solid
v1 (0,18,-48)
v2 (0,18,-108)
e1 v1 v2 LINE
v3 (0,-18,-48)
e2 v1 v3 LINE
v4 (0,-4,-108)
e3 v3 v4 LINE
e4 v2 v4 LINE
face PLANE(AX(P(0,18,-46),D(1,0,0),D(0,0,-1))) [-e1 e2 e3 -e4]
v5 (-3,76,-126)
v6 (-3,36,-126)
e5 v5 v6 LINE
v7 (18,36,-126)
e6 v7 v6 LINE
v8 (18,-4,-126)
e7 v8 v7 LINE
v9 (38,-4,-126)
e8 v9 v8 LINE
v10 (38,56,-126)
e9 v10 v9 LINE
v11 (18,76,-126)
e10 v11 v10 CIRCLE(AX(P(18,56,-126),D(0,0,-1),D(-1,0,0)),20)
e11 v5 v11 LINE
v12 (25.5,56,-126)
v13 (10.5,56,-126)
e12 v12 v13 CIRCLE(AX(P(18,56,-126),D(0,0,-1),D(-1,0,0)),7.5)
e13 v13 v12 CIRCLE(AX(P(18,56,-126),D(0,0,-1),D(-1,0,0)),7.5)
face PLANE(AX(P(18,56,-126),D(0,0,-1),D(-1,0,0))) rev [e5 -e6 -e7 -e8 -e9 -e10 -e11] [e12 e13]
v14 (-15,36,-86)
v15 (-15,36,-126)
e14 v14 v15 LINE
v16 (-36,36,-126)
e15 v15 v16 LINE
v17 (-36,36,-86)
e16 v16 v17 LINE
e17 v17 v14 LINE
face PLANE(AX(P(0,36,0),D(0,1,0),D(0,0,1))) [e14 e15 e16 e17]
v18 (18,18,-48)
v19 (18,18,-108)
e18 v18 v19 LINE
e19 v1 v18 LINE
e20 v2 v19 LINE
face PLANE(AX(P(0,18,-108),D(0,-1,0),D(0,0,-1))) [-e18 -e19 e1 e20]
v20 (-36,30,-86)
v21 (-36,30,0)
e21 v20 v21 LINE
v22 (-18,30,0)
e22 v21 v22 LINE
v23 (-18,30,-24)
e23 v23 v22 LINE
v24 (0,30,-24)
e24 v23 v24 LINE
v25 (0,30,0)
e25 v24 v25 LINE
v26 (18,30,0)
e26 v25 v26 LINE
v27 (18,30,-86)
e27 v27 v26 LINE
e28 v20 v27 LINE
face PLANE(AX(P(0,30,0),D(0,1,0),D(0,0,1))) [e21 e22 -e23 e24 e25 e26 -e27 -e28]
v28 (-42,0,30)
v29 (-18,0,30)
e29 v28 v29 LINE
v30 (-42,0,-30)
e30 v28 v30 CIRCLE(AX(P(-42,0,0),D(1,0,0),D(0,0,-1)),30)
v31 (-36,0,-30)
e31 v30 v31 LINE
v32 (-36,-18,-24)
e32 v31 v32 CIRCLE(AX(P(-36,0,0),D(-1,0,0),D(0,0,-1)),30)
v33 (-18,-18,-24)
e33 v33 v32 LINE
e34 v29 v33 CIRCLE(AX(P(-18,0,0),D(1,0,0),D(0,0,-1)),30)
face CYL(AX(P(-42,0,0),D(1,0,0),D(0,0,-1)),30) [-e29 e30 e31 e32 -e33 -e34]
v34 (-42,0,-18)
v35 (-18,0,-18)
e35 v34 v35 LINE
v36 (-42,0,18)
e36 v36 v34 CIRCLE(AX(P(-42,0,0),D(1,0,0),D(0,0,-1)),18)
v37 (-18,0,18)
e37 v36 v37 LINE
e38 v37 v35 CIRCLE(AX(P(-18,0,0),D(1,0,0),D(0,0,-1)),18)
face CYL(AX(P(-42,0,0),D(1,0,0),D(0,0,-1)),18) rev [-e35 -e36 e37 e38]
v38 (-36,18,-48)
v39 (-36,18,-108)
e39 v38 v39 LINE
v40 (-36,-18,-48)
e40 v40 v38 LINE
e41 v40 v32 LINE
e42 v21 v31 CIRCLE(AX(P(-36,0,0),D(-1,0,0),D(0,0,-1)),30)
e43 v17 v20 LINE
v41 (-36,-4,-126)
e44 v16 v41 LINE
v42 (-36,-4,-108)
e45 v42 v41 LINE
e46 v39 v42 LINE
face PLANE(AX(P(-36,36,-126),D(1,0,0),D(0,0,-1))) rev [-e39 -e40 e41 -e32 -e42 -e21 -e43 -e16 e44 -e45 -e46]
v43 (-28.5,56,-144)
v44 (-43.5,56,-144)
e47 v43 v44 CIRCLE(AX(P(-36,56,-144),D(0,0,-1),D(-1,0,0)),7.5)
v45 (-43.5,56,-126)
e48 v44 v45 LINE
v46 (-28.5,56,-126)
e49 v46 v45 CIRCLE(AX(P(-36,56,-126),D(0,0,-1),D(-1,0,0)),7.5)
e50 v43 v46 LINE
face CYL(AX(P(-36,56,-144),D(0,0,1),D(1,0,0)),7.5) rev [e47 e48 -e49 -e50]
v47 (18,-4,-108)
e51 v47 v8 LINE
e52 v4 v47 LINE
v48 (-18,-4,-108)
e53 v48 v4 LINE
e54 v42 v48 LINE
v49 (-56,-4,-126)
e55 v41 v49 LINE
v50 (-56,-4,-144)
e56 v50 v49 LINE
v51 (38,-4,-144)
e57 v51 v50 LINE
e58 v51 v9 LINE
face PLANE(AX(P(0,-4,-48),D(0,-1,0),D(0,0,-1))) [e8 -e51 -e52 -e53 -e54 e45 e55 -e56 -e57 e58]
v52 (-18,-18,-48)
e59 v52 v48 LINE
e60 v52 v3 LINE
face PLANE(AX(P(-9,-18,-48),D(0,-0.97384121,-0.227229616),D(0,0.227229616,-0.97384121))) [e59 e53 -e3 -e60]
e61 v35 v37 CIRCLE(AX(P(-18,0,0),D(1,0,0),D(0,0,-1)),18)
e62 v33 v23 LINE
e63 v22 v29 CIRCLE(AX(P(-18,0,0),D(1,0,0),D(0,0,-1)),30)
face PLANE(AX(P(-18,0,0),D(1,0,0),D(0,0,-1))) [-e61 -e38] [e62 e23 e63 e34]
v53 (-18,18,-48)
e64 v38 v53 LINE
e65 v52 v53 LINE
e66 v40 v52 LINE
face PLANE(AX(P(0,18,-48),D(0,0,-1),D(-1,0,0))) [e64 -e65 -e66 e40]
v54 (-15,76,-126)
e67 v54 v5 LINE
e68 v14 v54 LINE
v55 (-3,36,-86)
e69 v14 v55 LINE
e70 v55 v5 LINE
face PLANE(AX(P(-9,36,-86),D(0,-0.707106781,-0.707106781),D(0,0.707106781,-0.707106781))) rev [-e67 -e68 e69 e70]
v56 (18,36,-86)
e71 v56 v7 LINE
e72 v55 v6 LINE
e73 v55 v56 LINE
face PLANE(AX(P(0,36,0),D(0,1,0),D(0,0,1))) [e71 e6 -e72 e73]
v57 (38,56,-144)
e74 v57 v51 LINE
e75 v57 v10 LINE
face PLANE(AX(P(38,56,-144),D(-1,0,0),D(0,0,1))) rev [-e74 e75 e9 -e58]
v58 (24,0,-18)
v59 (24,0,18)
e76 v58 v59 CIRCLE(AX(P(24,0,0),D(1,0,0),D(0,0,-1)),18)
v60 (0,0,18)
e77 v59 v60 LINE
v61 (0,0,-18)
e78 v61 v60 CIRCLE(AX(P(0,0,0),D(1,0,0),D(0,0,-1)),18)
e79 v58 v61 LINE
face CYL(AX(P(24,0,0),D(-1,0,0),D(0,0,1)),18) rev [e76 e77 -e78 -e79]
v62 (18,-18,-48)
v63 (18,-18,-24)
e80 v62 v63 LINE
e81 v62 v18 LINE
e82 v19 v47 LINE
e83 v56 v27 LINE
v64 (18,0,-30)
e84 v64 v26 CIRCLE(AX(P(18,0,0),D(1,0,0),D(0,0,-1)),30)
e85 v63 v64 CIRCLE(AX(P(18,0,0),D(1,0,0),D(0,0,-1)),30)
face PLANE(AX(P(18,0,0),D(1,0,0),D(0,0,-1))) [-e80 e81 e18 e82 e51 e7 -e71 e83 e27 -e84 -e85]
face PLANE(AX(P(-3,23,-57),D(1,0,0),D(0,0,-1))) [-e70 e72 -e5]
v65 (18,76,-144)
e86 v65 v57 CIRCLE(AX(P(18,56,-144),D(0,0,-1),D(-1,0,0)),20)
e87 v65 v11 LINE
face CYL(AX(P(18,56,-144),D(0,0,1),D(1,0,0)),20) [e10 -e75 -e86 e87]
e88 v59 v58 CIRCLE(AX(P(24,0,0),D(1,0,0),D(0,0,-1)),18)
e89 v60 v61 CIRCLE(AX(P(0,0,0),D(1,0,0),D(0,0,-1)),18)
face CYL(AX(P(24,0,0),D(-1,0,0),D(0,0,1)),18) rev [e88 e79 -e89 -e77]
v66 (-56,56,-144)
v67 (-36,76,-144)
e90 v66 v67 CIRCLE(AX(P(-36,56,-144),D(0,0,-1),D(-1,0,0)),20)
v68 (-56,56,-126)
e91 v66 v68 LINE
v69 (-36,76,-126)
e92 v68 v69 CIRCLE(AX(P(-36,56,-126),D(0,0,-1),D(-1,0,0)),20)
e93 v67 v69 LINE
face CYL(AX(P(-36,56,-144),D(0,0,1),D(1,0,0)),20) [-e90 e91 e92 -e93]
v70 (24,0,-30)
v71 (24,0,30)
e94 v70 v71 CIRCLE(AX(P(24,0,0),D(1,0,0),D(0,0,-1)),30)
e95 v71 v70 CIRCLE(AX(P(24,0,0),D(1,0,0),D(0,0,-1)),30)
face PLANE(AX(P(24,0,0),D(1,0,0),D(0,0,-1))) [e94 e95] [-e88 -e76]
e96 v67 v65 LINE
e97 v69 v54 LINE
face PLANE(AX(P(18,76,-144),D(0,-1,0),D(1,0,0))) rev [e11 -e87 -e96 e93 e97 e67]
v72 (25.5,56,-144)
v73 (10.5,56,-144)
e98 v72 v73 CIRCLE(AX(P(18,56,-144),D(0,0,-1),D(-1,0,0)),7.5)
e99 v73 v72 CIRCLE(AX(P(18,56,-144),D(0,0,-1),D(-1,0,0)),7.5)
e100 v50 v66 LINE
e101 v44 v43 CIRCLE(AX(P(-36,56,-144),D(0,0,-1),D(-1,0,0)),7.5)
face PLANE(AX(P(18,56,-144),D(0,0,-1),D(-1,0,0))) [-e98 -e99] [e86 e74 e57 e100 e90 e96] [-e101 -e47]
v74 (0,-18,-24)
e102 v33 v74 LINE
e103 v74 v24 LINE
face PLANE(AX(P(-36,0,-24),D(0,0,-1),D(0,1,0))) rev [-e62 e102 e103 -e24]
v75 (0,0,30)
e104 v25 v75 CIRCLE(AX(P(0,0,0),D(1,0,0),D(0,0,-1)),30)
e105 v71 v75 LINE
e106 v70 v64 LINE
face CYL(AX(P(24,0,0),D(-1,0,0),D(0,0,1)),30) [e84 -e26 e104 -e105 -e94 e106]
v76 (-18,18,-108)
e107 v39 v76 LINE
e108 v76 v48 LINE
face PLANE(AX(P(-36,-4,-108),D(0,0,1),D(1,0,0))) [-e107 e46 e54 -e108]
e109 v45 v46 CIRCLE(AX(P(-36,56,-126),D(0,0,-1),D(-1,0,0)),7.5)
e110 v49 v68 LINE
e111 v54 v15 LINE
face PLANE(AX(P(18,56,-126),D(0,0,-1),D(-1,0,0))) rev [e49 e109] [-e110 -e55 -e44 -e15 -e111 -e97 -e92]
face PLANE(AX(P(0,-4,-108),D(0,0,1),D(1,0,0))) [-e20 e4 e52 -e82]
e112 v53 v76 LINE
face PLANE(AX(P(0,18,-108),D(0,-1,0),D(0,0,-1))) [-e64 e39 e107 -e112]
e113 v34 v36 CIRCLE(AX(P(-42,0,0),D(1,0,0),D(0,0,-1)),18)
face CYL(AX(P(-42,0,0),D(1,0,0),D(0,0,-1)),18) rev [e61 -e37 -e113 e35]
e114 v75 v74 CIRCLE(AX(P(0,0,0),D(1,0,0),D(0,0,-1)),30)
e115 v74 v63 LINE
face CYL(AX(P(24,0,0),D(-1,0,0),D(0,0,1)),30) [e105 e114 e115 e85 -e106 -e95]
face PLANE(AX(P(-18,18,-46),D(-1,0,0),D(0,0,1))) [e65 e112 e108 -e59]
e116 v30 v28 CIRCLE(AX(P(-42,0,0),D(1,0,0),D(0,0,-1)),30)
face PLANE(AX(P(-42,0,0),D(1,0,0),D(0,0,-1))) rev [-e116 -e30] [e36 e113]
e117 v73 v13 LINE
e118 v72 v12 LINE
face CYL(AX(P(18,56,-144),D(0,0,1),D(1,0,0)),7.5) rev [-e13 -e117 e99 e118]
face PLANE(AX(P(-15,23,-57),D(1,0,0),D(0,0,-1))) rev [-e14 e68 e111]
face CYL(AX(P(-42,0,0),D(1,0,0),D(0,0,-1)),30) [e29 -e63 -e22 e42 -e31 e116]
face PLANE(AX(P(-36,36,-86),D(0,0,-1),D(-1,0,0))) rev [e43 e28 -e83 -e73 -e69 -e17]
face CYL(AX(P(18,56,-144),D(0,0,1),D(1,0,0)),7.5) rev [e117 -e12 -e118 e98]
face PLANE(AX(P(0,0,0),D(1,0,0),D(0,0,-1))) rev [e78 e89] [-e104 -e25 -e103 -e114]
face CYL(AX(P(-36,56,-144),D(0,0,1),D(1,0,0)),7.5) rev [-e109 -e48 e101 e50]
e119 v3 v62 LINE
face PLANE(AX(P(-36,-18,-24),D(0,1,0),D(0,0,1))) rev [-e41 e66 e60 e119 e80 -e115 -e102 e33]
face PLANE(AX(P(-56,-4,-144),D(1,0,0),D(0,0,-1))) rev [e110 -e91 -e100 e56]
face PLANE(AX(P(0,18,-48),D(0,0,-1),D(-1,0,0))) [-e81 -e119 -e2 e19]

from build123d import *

# Parameters (mm, degrees)
CLEVIS_LUG_A_SKETCH_R       = 30
CLEVIS_LUG_A_SKETCH_R_2     = 18
CLEVIS_LUG_A_60X_36_DEPTH   = 24
CLEVIS_LUG_B_SKETCH_R       = 30
CLEVIS_LUG_B_SKETCH_R_2     = 18
CLEVIS_LUG_B_60X_36_DEPTH   = 24
ARM_START                   = -18
ARM_WEB_DEPTH               = 18
LUG_START                   = -18
LUG_BRIDGE_DEPTH            = 18
ARM_TOP_PLATE_SKETCH_W      = 54
ARM_TOP_PLATE_SKETCH_H      = 40
ARM_TOP_PLATE_6MM_DEPTH     = 6
ARM_SPINE_SKETCH_R          = 4
ARM_SPINE_54MM_DEPTH        = 54
ARM_BODY_SKETCH_W           = 18
ARM_BODY_SKETCH_H           = 22
ARM_BODY_80MM_DEPTH         = 80
ARM_SIDE_WEB_54MM_DEPTH     = 54
ARM_SLOT_SKETCH_W           = 24
ARM_SLOT_SKETCH_H           = 6
ARM_SLOT_CUT_DEPTH          = 27
ARM_RIB_18MM_REACH          = 137.133
ARM_RIB_SKETCH_WALL_W       = 333.878222312
ARM_RIB_SKETCH_WALL_H       = 18
MOUNTING_FLANGE_SKETCH_R    = 7.5
MOUNTING_FLANGE_DEPTH       = 18
FLANGE_GUSSET_12MM_REACH    = 171.473
FLANGE_GUSSET_SKETCH_WALL_W = 397.51396583
FLANGE_GUSSET_SKETCH_WALL_H = 12


with BuildPart() as part:
    # Clevis Lug A Sketch → Clevis Lug A Ø60xØ36 (new body)
    with BuildSketch(Plane(origin=(0, 0, 0), x_dir=(0, 0, -1), z_dir=(1, 0, 0))):
        Circle(CLEVIS_LUG_A_SKETCH_R)
        Circle(CLEVIS_LUG_A_SKETCH_R_2, mode=Mode.SUBTRACT)
    extrude(amount=CLEVIS_LUG_A_60X_36_DEPTH)

    # Arm Web Sketch → Arm Web (add)
    with BuildSketch(Plane(origin=(18, 0, 0), x_dir=(0, 0, -1), z_dir=(1, 0, 0)).offset(ARM_START)):
        with BuildLine():
            Line((0, 30), (48, 30))
            Line((48, 30), (126, 30))
            Line((126, 30), (126, -4))
            Line((126, -4), (108, -4))
            Line((108, -4), (108, 18))
            Line((108, 18), (48, 18))
            Line((48, 18), (48, -4))
            Line((48, -4), (17.549928775, -4))
            ThreePointArc((17.549928775, -4), (14.071247279, 11.22497216), (0, 18))
            Line((0, 18), (0, 30))
        make_face()
    extrude(amount=ARM_WEB_DEPTH)



with BuildPart() as body_2:
    # Clevis Lug B Sketch → Clevis Lug B Ø60xØ36 (new body)
    with BuildSketch(Plane(origin=(-18, 0, 0), x_dir=(0, 0, -1), z_dir=(1, 0, 0))):
        Circle(CLEVIS_LUG_B_SKETCH_R)
        Circle(CLEVIS_LUG_B_SKETCH_R_2, mode=Mode.SUBTRACT)
    extrude(amount=-CLEVIS_LUG_B_60X_36_DEPTH)

    # Lug Bridge Sketch → Lug Bridge (add)
    with BuildSketch(Plane(origin=(-18, 0, 0), x_dir=(0, 0, -1), z_dir=(1, 0, 0)).offset(LUG_START)):
        with BuildLine():
            Line((0, 30), (126, 30))
            Line((126, 30), (126, -4))
            Line((126, -4), (108, -4))
            Line((108, -4), (108, 18))
            Line((108, 18), (48, 18))
            Line((48, 18), (48, -4))
            Line((48, -4), (17.549928775, -4))
            ThreePointArc((17.549928775, -4), (14.071247279, 11.22497216), (0, 18))
            Line((0, 18), (0, 30))
        make_face()
    extrude(amount=LUG_BRIDGE_DEPTH)


with BuildPart() as part_1:
    add(part.part)

    add(body_2.part)  # Arm Top Plate 6mm merges body 2
    # Arm Top Plate Sketch → Arm Top Plate 6mm (add)
    with BuildSketch(Plane(origin=(0, 30, 0), x_dir=(1, 0, 0), z_dir=(0, 1, 0))):
        with Locations((-9, 106)):
            Rectangle(ARM_TOP_PLATE_SKETCH_W, ARM_TOP_PLATE_SKETCH_H)
    extrude(amount=ARM_TOP_PLATE_6MM_DEPTH)

    # Arm Spine Sketch → Arm Spine 54mm (add)
    with BuildSketch(Plane(origin=(18, 0, 0), x_dir=(0, 0, -1), z_dir=(1, 0, 0))):
        with BuildLine():
            ThreePointArc((24, 18), (29.030770743, 7.564016794), (29.732137495, -4))
            Line((29.732137495, -4), (48, -4))
            Line((48, -4), (48, 18))
            Line((48, 18), (108, 18))
            Line((108, 18), (126, 18))
            Line((126, 18), (126, 30))
            Line((126, 30), (86, 30))
            Line((86, 30), (24, 30))
            Line((24, 30), (24, 18))
        make_face()
        with BuildLine():
            Line((24, 18), (24, -4))
            Line((24, -4), (29.732137495, -4))
            ThreePointArc((29.732137495, -4), (29.030770743, 7.564016794), (24, 18))
        make_face()
        Circle(ARM_SPINE_SKETCH_R)
    extrude(amount=-ARM_SPINE_54MM_DEPTH)


with BuildPart() as arm_spine_54mm_kept_piece:
    # of the separate pieces the step leaves, the one the design keeps (arm_spine_54mm_pieces_kept)
    add(part_1.part.solids().sort_by_distance((-36, 36, -126))[0])

    # Arm Body Sketch → Arm Body 80mm (add)
    with BuildSketch(Plane(origin=(0, 0, -126), x_dir=(-1, 0, 0), z_dir=(0, 0, -1))):
        with Locations((9, 7)):
            Rectangle(ARM_BODY_SKETCH_W, ARM_BODY_SKETCH_H)
    extrude(amount=-ARM_BODY_80MM_DEPTH)

    # Arm Side Web Sketch → Arm Side Web 54mm (add)
    with BuildSketch(Plane(origin=(18, 0, 0), x_dir=(0, 0, -1), z_dir=(1, 0, 0))):
        Polygon((48, -4), (48, -24), (24, -24), (24, 6), (48, 6), align=None)
    extrude(amount=-ARM_SIDE_WEB_54MM_DEPTH)

    # Arm Slot Sketch → Arm Slot Cut (cut, symmetric)
    with BuildSketch(Plane(origin=(-9, 0, 0), x_dir=(0, 0, -1), z_dir=(1, 0, 0))):
        with Locations((36, -21)):
            Rectangle(ARM_SLOT_SKETCH_W, ARM_SLOT_SKETCH_H)
    extrude(amount=ARM_SLOT_CUT_DEPTH, both=True, mode=Mode.SUBTRACT)

    # Arm Rib Sketch wall → Arm Rib 18mm (add, up to next)
    with BuildSketch(Plane(origin=(-9, -11, -78), x_dir=(0, 0.227229615606, -0.973841209742), z_dir=(0, 0.973841209742, 0.227229615606)), mode=Mode.PRIVATE) as arm_rib_18mm_sk1:
        Rectangle(ARM_RIB_SKETCH_WALL_W, ARM_RIB_SKETCH_WALL_H)
    arm_rib_18mm_tool1 = extrude(arm_rib_18mm_sk1.sketch, amount=ARM_RIB_18MM_REACH, mode=Mode.PRIVATE) - arm_spine_54mm_kept_piece.part
    add(arm_rib_18mm_tool1.solids().sort_by_distance((-9, -11, -78))[0])

    # Mounting Flange Sketch → Mounting Flange (add)
    with BuildSketch(Plane(origin=(0, 0, -126), x_dir=(-1, 0, 0), z_dir=(0, 0, -1))):
        with BuildLine():
            Line((-18, 76), (36, 76))
            ThreePointArc((36, 76), (50.142135624, 70.142135624), (56, 56))
            Line((56, 56), (56, -4))
            Line((56, -4), (-38, -4))
            Line((-38, -4), (-38, 56))
            ThreePointArc((-38, 56), (-32.142135624, 70.142135624), (-18, 76))
        make_face()
        with Locations((-18, 56)):
            Circle(MOUNTING_FLANGE_SKETCH_R, mode=Mode.SUBTRACT)
        with Locations((36, 56)):
            Circle(MOUNTING_FLANGE_SKETCH_R, mode=Mode.SUBTRACT)
    extrude(amount=MOUNTING_FLANGE_DEPTH)

    # Flange Gusset Sketch wall → Flange Gusset 12mm (add, up to next)
    with BuildSketch(Plane(origin=(-9, 56, -106), x_dir=(0, 0.707106781187, -0.707106781187), z_dir=(0, 0.707106781187, 0.707106781187)), mode=Mode.PRIVATE) as flange_gusset_12mm_sk1:
        Rectangle(FLANGE_GUSSET_SKETCH_WALL_W, FLANGE_GUSSET_SKETCH_WALL_H)
    flange_gusset_12mm_tool1 = extrude(flange_gusset_12mm_sk1.sketch, amount=-FLANGE_GUSSET_12MM_REACH, mode=Mode.PRIVATE) - arm_spine_54mm_kept_piece.part
    add(flange_gusset_12mm_tool1.solids().sort_by_distance((-9, 56, -106))[0])


solid = arm_spine_54mm_kept_piece.part
